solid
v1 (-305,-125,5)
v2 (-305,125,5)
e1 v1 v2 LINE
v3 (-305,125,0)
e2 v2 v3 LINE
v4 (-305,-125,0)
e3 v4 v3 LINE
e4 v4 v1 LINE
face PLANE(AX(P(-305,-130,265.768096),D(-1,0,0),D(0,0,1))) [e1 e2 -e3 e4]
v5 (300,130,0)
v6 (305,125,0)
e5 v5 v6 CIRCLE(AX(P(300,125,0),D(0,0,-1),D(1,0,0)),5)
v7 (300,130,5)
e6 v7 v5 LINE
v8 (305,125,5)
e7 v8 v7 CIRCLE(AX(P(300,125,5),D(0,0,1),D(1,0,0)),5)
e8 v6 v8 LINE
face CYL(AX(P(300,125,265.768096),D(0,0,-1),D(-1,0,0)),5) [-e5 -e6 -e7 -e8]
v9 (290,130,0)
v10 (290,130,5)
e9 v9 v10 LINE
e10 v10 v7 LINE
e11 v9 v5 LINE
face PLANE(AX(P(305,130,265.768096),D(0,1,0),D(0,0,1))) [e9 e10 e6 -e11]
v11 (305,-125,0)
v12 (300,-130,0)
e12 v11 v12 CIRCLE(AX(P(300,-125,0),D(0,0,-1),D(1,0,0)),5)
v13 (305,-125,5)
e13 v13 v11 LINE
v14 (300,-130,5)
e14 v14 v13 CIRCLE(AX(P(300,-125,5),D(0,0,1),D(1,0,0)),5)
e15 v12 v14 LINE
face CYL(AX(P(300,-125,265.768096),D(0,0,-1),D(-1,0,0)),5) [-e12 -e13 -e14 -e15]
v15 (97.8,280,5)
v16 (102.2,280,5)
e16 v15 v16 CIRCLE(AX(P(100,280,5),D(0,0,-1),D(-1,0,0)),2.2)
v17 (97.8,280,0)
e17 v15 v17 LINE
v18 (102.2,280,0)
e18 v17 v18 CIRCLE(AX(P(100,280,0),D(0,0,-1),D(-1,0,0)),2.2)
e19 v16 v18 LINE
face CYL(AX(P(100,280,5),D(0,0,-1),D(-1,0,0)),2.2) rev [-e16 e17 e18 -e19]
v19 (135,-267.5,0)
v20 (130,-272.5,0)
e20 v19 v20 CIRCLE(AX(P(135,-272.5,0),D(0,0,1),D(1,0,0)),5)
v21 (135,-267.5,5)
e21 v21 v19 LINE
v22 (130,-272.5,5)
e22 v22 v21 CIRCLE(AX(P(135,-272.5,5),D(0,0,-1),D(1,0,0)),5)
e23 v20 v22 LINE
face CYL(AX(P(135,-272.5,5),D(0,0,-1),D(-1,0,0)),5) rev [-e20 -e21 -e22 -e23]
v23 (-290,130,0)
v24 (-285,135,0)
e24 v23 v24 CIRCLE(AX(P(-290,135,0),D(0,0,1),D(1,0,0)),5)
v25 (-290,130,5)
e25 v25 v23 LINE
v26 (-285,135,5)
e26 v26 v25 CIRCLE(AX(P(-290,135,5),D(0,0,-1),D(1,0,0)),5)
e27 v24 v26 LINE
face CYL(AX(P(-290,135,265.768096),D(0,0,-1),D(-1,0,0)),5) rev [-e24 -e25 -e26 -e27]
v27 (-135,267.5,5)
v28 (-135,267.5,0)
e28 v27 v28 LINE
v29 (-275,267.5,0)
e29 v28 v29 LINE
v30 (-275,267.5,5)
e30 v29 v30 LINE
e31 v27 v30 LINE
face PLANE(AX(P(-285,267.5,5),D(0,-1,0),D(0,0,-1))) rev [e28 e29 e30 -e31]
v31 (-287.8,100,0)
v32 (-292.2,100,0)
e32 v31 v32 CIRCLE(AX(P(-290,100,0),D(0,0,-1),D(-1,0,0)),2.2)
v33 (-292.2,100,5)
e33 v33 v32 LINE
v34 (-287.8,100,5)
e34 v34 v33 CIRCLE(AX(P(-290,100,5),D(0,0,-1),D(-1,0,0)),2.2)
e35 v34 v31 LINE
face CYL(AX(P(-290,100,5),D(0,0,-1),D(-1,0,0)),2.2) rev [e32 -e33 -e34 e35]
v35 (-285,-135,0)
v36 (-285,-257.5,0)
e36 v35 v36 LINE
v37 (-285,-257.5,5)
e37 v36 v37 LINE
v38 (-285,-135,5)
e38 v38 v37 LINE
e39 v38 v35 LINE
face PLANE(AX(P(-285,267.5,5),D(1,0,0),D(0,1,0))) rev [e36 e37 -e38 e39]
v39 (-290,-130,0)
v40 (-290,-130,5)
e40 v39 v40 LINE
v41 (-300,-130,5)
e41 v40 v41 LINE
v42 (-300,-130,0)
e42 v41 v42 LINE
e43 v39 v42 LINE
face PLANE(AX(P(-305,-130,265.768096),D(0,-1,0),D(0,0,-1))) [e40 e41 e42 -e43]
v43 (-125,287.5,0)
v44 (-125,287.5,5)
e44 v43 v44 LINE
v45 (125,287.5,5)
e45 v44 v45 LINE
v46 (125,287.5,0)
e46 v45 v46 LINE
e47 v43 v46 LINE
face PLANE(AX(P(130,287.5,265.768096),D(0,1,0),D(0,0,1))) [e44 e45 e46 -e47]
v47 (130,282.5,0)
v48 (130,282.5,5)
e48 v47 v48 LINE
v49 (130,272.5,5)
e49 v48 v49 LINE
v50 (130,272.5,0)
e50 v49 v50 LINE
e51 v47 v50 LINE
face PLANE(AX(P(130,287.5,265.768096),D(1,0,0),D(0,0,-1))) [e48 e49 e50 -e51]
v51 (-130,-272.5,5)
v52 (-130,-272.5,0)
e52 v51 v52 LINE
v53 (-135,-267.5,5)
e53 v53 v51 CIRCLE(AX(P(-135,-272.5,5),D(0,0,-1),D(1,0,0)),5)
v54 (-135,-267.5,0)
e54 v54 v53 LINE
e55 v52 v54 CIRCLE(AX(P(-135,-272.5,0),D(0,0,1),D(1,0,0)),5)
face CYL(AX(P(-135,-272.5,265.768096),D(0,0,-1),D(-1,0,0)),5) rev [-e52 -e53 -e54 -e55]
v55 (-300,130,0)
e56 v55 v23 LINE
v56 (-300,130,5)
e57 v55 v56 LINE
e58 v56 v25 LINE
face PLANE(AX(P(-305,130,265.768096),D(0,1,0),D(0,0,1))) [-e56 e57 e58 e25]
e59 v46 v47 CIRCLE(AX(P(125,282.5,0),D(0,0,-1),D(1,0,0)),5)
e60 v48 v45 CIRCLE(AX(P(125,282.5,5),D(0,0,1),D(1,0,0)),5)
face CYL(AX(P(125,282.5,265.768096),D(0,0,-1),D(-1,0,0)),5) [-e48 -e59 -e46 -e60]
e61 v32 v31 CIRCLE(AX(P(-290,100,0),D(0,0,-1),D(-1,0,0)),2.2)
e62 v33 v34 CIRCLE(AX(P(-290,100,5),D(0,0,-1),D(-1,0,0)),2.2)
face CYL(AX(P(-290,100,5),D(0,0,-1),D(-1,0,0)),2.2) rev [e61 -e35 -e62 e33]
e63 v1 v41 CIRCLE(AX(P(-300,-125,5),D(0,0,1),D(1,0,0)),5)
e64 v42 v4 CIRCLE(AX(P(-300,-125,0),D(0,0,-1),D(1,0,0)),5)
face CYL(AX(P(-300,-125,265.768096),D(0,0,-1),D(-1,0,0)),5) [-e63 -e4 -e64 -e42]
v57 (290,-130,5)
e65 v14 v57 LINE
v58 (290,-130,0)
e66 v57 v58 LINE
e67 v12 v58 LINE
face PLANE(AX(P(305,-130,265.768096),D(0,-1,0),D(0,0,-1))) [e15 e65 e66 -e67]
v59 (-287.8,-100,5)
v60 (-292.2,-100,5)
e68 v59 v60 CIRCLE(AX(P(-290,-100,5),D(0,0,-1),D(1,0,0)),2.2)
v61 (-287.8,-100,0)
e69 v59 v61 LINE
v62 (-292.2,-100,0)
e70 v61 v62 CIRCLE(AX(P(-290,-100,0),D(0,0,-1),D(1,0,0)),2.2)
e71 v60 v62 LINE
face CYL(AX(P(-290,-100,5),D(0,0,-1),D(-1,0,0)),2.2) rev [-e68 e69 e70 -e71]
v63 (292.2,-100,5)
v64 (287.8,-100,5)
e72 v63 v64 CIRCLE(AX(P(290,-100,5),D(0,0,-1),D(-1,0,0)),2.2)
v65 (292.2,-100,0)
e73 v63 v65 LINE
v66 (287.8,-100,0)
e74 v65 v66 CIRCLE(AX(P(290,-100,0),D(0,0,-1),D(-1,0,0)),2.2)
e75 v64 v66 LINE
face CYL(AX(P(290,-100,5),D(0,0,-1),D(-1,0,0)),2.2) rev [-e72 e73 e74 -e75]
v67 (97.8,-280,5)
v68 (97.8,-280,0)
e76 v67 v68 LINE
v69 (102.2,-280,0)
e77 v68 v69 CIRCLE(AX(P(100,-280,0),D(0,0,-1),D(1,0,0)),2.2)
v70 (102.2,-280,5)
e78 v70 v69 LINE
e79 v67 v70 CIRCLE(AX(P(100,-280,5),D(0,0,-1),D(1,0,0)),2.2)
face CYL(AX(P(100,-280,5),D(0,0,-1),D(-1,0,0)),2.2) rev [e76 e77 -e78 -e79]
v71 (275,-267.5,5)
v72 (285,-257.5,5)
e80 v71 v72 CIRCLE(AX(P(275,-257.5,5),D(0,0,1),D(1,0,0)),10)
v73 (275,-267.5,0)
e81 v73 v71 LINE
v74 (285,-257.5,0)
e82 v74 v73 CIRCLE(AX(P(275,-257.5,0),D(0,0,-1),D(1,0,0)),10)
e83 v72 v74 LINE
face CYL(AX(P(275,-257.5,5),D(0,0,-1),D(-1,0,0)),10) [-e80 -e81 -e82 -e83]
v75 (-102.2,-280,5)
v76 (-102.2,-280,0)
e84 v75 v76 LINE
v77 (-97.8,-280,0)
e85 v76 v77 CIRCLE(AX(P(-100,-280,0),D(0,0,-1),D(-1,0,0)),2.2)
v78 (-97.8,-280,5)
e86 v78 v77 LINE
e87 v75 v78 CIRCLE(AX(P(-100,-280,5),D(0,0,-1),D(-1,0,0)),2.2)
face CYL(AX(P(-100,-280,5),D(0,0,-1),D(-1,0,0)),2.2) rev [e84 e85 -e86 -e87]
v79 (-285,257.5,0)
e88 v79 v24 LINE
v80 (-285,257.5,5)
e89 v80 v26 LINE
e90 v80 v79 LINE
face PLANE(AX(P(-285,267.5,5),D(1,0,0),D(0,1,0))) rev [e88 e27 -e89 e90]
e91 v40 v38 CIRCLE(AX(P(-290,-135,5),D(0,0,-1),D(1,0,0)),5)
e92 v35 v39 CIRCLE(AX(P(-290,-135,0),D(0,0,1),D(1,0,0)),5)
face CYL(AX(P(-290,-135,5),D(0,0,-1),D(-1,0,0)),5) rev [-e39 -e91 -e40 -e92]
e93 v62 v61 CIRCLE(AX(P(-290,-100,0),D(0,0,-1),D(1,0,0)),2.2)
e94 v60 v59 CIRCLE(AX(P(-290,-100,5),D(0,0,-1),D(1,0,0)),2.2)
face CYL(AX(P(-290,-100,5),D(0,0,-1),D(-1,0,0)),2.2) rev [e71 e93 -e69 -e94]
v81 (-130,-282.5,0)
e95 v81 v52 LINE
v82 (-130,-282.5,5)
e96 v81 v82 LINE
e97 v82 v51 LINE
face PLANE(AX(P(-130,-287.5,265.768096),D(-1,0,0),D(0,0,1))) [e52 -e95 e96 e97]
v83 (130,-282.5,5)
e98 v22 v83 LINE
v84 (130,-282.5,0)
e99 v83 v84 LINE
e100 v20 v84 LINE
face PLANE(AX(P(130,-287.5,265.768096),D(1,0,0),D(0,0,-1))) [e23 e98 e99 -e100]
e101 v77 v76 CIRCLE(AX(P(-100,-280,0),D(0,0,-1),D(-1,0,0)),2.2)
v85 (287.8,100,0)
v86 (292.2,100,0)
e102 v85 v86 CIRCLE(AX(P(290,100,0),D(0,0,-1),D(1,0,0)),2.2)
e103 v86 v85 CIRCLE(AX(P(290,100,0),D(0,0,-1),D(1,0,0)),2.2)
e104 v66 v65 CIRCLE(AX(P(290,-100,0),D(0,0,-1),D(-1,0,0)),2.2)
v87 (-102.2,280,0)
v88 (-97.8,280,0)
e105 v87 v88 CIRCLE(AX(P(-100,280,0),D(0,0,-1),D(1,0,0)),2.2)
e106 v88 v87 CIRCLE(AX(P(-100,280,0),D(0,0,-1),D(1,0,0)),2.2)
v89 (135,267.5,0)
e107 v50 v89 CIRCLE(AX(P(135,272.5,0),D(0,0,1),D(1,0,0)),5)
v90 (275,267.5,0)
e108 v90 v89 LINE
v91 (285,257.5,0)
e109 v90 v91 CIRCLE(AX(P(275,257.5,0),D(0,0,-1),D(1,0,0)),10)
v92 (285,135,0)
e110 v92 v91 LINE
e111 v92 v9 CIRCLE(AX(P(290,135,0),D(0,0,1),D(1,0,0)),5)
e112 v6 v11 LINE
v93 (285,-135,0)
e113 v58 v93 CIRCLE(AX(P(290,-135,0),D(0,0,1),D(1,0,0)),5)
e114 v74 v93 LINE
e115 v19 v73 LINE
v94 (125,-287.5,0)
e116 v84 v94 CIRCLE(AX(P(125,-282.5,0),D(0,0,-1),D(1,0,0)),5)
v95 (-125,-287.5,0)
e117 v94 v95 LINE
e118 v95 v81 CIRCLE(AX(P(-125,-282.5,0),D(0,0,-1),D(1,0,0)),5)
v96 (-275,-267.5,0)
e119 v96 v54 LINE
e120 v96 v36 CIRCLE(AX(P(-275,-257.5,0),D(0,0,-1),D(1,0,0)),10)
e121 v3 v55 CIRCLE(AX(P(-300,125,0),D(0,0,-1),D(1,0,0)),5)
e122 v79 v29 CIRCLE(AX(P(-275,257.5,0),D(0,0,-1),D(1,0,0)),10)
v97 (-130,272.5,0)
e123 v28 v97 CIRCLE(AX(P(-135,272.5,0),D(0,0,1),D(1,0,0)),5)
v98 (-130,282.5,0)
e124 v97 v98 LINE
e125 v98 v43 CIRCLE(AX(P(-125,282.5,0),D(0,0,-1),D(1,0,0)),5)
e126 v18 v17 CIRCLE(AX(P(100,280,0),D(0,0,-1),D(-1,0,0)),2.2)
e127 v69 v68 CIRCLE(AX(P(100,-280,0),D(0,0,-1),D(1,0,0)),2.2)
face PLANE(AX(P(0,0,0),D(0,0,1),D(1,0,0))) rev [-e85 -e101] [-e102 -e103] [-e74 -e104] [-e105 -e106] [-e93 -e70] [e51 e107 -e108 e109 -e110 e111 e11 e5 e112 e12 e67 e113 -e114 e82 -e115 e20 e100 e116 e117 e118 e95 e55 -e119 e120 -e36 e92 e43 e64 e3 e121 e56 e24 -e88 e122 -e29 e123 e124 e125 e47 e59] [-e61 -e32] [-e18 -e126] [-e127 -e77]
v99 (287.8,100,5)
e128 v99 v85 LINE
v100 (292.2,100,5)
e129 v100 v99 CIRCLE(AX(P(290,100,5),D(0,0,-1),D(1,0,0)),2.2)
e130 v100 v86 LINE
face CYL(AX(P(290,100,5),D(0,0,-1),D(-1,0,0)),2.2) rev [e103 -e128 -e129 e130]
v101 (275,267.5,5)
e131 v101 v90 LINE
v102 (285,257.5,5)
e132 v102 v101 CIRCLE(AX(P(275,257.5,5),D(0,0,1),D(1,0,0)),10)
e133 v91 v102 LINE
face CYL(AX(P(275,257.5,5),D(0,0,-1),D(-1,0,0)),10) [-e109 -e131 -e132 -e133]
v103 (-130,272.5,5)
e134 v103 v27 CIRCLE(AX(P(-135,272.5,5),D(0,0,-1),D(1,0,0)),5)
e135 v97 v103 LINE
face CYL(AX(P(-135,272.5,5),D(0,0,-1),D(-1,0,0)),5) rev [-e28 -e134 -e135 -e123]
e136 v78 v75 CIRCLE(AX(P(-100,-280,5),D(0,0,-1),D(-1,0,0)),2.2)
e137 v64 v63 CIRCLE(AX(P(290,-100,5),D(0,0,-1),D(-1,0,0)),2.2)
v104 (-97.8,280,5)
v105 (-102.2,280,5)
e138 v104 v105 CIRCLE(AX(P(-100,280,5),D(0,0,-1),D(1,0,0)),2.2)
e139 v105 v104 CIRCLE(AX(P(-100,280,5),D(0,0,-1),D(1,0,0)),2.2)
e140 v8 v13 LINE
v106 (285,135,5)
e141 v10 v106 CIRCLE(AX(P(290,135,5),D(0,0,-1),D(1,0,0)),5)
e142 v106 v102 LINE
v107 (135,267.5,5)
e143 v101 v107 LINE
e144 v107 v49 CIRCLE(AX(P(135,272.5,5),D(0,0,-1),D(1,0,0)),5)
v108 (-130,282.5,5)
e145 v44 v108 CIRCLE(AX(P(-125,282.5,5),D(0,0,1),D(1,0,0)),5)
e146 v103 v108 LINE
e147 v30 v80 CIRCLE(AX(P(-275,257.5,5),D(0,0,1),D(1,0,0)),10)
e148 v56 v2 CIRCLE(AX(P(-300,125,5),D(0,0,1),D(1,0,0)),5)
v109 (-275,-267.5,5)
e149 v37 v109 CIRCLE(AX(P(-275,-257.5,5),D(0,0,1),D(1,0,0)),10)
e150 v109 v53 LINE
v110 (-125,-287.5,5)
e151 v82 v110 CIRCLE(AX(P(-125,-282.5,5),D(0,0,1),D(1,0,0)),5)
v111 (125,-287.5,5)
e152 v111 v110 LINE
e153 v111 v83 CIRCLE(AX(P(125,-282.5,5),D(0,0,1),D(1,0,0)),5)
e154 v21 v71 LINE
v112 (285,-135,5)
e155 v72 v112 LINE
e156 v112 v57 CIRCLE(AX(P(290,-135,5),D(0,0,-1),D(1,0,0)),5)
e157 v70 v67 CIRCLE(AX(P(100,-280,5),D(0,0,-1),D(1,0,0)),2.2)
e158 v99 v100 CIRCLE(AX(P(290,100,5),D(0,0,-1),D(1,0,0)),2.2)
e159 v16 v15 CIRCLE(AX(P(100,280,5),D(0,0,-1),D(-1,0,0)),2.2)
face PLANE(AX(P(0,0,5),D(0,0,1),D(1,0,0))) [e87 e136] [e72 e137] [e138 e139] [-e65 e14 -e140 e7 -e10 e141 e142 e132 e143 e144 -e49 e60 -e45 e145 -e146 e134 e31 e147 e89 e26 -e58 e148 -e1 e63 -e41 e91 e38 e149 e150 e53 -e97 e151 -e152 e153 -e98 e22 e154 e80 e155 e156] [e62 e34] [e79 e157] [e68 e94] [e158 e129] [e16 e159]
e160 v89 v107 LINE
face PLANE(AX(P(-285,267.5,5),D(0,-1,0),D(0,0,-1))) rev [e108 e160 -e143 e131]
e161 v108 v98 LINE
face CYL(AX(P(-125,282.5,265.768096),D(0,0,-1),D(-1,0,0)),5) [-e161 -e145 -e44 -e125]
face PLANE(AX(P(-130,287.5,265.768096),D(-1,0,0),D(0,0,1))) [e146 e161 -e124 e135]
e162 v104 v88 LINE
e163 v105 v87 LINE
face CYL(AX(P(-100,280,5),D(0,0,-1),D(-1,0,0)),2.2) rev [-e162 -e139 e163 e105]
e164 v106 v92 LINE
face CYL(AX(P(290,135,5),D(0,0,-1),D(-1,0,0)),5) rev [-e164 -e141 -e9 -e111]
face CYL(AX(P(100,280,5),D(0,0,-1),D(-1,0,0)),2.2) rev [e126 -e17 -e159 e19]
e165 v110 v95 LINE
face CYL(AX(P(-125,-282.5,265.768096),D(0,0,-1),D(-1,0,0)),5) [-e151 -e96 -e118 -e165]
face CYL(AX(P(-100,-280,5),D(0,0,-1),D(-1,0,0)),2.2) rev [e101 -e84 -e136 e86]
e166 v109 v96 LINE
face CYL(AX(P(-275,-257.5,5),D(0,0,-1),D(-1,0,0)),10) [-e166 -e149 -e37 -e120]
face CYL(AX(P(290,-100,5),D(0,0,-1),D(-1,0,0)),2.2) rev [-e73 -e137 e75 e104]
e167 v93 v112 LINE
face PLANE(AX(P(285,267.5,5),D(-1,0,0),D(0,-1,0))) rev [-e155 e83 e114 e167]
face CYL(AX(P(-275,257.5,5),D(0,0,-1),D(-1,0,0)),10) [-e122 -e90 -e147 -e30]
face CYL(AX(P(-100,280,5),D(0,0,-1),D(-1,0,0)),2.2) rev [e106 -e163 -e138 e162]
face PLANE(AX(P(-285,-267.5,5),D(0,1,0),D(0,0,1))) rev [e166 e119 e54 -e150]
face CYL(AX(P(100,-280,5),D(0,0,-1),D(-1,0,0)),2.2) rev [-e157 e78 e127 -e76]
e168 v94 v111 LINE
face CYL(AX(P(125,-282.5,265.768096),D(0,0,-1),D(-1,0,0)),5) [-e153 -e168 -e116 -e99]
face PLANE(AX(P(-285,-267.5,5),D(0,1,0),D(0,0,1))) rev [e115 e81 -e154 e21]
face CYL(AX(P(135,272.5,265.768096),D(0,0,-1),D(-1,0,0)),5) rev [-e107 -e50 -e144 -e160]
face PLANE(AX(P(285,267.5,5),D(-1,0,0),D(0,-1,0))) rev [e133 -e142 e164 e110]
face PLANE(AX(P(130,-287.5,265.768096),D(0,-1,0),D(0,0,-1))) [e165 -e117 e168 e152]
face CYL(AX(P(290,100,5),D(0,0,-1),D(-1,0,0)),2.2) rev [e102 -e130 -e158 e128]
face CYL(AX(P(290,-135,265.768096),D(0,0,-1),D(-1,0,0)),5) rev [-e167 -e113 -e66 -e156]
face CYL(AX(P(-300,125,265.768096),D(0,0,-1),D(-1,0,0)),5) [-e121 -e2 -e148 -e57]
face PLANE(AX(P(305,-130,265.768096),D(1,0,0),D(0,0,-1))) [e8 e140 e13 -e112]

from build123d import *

# Parameters (mm, degrees)
SKETCH_1_W          = 570
SKETCH_1_H          = 535
EXTRUDE_1_DEPTH     = 5
FILLET_1_R          = 10
SKETCH_4_W          = 260
SKETCH_4_H          = 20
SKETCH_4_W_2        = 20
SKETCH_4_H_2        = 260
EXTRUDE_2_DEPTH     = 5
SKETCH_5_R          = 2.2
CUT_EXTRUDE_2_DEPTH = 420.17329352
FILLET_2_R          = 5


with BuildPart() as part:
    # 草图1 → 凸台-拉伸1 (new body)
    with BuildSketch(Plane.XY):
        Rectangle(SKETCH_1_W, SKETCH_1_H)
    extrude(amount=EXTRUDE_1_DEPTH)

    # 圆角1
    fillet_1_edges = [part.edges().sort_by_distance(p)[0] for p in [
        (285, -267.5, 2.5),
        (-285, -267.5, 2.5),
        (-285, 267.5, 2.5),
        (285, 267.5, 2.5),
    ]]
    fillet(fillet_1_edges, radius=FILLET_1_R)

    # 草图4 → 凸台-拉伸2 (add)
    with BuildSketch(Plane(origin=(0, 0, 0), x_dir=(-1, 0, 0), z_dir=(0, 0, -1))):
        with Locations((0, 277.5)):
            Rectangle(SKETCH_4_W, SKETCH_4_H)
        with Locations((295, 0)):
            Rectangle(SKETCH_4_W_2, SKETCH_4_H_2)
        with Locations((0, -277.5)):
            Rectangle(SKETCH_4_W, SKETCH_4_H)
        with Locations((-295, 0)):
            Rectangle(SKETCH_4_W_2, SKETCH_4_H_2)
    extrude(amount=-EXTRUDE_2_DEPTH)

    # 草图5 → 切除-拉伸2 (cut, through all)
    with BuildSketch(Plane(origin=(0, 0, 0), x_dir=(-1, 0, 0), z_dir=(0, 0, -1))):
        with Locations((-100, 280)):
            Circle(SKETCH_5_R)
        with Locations(Location((100, 280, 0), (0, 0, 180))):
            Circle(SKETCH_5_R)
        with Locations((290, 100)):
            Circle(SKETCH_5_R)
        with Locations(Location((290, -100, 0), (0, 0, 180))):
            Circle(SKETCH_5_R)
        with Locations((100, -280)):
            Circle(SKETCH_5_R)
        with Locations(Location((-100, -280, 0), (0, 0, 180))):
            Circle(SKETCH_5_R)
        with Locations((-290, -100)):
            Circle(SKETCH_5_R)
        with Locations(Location((-290, 100, 0), (0, 0, 180))):
            Circle(SKETCH_5_R)
    extrude(amount=-CUT_EXTRUDE_2_DEPTH, mode=Mode.SUBTRACT)

    # 圆角2
    fillet_2_edges = [part.edges().sort_by_distance(p)[0] for p in [
        (130, 287.5, 2.5),
        (130, 267.5, 2.5),
        (-130, 267.5, 2.5),
        (-130, 287.5, 2.5),
        (-305, -130, 2.5),
        (-305, 130, 2.5),
        (-285, 130, 2.5),
        (-285, -130, 2.5),
        (-130, -287.5, 2.5),
        (-130, -267.5, 2.5),
        (130, -267.5, 2.5),
        (130, -287.5, 2.5),
        (285, -130, 2.5),
        (285, 130, 2.5),
        (305, 130, 2.5),
        (305, -130, 2.5),
    ]]
    fillet(fillet_2_edges, radius=FILLET_2_R)


solid = part.part
